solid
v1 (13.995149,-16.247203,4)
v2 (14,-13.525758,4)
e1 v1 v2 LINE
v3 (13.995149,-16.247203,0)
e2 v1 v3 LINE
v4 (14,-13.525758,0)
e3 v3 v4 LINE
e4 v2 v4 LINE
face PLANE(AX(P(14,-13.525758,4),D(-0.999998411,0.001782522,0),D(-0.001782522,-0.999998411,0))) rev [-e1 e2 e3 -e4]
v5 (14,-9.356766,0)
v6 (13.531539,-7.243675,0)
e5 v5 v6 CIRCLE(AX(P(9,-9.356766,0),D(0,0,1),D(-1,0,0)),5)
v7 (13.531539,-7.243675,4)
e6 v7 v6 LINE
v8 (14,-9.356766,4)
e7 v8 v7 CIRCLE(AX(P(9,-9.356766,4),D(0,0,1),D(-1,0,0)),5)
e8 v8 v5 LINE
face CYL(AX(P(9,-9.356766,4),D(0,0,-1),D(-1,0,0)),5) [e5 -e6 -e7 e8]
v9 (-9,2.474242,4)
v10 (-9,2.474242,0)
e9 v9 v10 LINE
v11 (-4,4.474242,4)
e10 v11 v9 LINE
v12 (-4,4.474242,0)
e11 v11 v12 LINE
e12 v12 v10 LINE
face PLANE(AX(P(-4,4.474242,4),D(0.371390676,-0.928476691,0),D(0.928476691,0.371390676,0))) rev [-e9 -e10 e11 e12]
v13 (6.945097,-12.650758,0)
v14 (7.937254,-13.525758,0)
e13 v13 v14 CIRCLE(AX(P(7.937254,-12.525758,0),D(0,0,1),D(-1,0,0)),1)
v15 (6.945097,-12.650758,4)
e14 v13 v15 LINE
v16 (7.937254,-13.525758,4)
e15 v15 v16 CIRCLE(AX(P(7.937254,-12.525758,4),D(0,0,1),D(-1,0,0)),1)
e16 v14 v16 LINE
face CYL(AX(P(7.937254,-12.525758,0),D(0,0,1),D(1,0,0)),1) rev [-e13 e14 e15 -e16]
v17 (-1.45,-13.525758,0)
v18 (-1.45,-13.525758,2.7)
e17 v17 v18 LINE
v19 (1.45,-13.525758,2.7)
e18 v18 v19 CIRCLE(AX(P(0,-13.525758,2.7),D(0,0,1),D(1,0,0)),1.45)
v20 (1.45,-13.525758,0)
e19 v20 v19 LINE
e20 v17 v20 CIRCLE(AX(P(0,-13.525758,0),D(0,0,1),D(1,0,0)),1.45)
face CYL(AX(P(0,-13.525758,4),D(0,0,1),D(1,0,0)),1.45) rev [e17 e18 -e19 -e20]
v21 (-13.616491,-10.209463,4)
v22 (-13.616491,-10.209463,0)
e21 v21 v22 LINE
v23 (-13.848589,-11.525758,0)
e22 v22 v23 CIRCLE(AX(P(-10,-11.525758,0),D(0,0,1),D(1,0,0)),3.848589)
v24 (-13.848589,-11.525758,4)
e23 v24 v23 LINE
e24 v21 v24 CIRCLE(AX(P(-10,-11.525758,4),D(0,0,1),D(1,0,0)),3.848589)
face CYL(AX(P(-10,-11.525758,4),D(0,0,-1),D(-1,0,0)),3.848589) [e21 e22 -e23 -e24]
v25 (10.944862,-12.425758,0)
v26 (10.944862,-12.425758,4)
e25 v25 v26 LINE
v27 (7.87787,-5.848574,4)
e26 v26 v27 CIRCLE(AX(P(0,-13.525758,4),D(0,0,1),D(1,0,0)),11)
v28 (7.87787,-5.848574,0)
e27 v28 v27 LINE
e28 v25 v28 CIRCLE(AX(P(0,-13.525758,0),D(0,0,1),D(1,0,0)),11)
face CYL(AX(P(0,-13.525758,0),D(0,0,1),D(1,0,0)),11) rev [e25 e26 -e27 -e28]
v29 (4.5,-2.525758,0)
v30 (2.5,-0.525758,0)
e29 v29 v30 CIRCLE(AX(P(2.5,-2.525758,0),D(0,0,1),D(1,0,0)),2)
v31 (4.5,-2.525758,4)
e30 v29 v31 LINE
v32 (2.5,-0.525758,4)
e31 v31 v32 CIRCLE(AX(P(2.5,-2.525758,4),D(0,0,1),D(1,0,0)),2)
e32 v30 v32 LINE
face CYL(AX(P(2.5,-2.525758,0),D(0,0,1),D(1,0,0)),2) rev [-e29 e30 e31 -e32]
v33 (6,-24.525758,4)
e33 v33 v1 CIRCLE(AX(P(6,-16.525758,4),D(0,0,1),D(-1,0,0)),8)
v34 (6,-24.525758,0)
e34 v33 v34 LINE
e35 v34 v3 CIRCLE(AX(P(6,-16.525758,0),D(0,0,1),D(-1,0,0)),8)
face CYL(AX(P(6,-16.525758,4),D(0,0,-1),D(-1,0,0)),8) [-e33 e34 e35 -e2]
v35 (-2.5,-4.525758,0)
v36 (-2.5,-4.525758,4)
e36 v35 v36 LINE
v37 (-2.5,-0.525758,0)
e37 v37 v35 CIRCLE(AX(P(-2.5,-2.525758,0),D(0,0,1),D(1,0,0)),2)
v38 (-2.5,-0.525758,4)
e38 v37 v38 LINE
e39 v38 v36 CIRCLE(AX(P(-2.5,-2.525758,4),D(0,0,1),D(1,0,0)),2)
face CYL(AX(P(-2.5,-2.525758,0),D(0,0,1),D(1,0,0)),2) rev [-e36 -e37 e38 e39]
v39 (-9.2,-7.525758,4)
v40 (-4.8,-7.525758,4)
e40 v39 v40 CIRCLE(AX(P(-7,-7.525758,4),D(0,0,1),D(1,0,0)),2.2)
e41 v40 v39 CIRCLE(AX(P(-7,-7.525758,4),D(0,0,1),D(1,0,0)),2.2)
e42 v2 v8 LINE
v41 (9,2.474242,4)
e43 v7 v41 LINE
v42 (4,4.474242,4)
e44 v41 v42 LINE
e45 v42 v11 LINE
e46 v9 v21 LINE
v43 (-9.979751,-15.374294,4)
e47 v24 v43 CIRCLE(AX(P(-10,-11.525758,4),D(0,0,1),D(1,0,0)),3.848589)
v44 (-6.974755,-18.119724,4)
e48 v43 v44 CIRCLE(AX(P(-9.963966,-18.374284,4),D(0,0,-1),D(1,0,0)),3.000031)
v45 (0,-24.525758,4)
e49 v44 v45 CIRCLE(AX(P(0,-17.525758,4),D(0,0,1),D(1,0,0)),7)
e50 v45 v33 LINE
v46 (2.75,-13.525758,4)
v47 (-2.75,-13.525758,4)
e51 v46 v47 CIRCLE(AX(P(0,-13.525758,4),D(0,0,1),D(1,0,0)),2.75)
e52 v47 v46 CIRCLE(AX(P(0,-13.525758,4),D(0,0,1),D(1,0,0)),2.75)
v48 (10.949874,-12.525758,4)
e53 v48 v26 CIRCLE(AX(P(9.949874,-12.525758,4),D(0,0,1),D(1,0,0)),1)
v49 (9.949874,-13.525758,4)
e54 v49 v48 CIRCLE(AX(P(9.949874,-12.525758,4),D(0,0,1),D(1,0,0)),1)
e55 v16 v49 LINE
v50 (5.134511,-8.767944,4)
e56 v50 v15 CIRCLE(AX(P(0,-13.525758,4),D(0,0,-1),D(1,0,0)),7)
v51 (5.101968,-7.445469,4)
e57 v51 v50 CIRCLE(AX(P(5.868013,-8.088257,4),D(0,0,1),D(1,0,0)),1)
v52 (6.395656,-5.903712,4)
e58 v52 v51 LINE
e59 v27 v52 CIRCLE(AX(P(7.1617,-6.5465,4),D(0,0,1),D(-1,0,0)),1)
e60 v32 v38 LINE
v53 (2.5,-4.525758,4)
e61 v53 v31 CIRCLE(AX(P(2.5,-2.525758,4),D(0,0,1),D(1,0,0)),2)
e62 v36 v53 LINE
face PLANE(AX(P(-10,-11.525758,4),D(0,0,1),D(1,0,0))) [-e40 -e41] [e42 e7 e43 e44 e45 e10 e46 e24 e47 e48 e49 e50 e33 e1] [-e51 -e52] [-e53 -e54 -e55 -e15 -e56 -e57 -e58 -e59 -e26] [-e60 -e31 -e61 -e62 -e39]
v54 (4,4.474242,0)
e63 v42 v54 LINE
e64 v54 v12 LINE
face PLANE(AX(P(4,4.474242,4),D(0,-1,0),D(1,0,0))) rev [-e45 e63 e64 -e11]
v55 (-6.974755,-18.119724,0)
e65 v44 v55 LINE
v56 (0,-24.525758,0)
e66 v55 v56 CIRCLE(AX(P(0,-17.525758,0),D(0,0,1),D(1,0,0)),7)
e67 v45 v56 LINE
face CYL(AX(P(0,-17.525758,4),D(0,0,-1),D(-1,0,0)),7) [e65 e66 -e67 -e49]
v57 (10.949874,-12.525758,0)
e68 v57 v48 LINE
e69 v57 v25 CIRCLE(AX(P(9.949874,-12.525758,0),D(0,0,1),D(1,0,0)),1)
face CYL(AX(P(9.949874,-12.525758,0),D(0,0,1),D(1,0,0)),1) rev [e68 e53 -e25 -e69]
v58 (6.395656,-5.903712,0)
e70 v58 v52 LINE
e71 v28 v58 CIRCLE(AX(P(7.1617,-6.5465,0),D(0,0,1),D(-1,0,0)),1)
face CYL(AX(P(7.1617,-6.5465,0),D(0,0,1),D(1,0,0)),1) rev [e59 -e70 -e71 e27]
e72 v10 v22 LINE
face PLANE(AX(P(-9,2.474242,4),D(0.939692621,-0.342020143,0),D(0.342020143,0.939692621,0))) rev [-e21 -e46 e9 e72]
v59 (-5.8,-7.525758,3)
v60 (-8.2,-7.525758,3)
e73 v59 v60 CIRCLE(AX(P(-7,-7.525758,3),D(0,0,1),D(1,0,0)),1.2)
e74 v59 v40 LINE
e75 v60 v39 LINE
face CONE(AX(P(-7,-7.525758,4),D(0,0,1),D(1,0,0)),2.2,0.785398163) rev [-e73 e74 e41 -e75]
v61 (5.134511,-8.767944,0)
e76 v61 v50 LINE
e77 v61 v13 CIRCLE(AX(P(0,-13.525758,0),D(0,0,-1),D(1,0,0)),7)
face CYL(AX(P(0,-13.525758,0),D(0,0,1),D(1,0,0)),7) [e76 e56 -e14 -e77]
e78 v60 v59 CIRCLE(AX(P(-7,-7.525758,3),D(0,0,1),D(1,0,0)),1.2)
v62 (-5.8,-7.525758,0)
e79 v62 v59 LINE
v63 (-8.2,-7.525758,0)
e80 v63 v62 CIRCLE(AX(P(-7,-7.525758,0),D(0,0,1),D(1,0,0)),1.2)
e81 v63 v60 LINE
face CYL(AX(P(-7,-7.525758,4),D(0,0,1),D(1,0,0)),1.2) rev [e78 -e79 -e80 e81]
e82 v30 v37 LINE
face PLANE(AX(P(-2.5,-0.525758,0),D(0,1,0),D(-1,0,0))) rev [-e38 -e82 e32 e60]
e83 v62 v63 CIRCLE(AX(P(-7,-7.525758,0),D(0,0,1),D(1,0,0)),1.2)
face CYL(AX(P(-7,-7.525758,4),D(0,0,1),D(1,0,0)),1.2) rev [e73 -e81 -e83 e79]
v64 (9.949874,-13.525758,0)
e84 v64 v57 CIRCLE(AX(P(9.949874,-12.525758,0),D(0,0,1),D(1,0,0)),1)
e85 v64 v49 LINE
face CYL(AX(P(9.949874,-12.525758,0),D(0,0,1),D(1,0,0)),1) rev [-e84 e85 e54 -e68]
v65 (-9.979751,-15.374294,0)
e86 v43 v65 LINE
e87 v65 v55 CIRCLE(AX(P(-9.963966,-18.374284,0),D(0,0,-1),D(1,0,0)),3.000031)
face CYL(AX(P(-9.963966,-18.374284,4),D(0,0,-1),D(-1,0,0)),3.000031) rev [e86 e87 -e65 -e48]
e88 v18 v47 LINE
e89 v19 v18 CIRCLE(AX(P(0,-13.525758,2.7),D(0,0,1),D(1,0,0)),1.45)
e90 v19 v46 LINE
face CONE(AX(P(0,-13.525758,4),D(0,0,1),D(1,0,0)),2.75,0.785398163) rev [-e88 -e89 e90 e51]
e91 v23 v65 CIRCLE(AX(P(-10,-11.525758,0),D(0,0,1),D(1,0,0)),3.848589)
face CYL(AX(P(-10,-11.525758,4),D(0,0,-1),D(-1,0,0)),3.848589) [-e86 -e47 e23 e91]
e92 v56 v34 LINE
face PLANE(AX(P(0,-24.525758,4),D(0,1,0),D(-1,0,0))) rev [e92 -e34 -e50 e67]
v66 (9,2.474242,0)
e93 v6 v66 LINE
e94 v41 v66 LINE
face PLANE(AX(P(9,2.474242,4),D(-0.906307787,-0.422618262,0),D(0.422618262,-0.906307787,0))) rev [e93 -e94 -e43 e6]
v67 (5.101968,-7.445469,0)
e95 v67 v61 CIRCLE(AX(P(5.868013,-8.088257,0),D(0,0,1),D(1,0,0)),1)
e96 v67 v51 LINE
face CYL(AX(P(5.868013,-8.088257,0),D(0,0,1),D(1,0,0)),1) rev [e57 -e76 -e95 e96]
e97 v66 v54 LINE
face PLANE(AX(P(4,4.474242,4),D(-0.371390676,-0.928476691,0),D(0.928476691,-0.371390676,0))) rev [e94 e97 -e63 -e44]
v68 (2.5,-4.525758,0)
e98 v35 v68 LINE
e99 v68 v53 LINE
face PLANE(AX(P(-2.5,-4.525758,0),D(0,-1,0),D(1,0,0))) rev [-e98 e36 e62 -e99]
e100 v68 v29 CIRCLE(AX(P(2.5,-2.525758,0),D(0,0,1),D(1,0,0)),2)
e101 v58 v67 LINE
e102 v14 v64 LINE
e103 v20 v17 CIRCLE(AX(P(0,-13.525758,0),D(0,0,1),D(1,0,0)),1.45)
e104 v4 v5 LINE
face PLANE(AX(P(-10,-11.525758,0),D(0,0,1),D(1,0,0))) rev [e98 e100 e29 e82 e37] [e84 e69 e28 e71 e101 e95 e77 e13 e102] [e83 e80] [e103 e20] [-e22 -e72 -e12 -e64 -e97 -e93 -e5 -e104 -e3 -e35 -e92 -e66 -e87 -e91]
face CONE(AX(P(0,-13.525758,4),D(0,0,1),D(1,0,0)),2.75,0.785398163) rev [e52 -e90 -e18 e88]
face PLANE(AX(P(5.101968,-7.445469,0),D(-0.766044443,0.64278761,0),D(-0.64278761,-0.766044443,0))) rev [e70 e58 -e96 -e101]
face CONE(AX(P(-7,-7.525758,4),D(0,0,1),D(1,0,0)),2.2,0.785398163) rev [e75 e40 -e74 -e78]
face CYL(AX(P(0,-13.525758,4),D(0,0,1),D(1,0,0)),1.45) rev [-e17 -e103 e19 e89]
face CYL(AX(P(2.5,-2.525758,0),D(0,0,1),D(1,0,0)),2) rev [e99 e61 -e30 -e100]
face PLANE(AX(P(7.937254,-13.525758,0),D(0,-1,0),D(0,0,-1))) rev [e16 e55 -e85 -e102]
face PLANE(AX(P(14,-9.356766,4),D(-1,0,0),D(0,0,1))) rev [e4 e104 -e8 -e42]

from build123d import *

# Parameters (mm, degrees)
CAM_PLATE_4MM_DEPTH       = 4
SLOTS_CUT_DEPTH           = 4
CSK_HOLE_M2_5_D           = 2.9
CSK_HOLE_M2_5_DEPTH       = 29
CSK_HOLE_M2_5_CSINK_D     = 5.5
CSK_HOLE_M2_5_CSINK_ANGLE = 90
CSK_HOLE_M2_5_TIP         = 0.871247898
CSK_HOLE_M2_D             = 2.4
CSK_HOLE_M2_DEPTH         = 29
CSK_HOLE_M2_CSINK_D       = 4.4
CSK_HOLE_M2_CSINK_ANGLE   = 90
CSK_HOLE_M2_TIP           = 0.721032743


with BuildPart() as part:
    # Cam Plate Profile Sketch → Cam Plate 4mm (new body)
    with BuildSketch(Plane.XY):
        with BuildLine():
            Line((4, 4.474241718), (-4, 4.474241718))
            Line((-4, 4.474241718), (-9, 2.474241718))
            Line((-9, 2.474241718), (-13.616491046, -10.209463189))
            ThreePointArc((-13.616491046, -10.209463189), (-13.146761684, -13.741504469), (-9.979750738, -15.374294397))
            ThreePointArc((-9.979750738, -15.374294397), (-7.940438794, -16.159442387), (-6.974754793, -18.11972425))
            ThreePointArc((-6.974754793, -18.11972425), (-4.735094414, -22.681229249), (0, -24.525758282))
            Line((0, -24.525758282), (6, -24.525758282))
            ThreePointArc((6, -24.525758282), (11.754495804, -22.083255744), (13.995148957, -16.247202791))
            Line((13.995148957, -16.247202791), (14, -13.525758282))
            Line((14, -13.525758282), (14, -9.356766198))
            ThreePointArc((14, -9.356766198), (13.881480036, -8.274568128), (13.531538935, -7.243674889))
            Line((13.531538935, -7.243674889), (9, 2.474241718))
            Line((9, 2.474241718), (4, 4.474241718))
        make_face()
    extrude(amount=CAM_PLATE_4MM_DEPTH)

    # Slot Profiles Sketch → Slots Cut (cut)
    with BuildSketch(Plane.XY.offset(4)):
        with BuildLine():
            Line((-2.5, -0.525758282), (2.5, -0.525758282))
            ThreePointArc((2.5, -0.525758282), (4.5, -2.525758282), (2.5, -4.525758282))
            Line((2.5, -4.525758282), (-2.5, -4.525758282))
            ThreePointArc((-2.5, -4.525758282), (-4.5, -2.525758282), (-2.5, -0.525758282))
        make_face()
        with BuildLine():
            Line((5.101968483, -7.445469013), (6.395655964, -5.90371231))
            ThreePointArc((6.395655964, -5.90371231), (7.124526222, -5.547191119), (7.877870447, -5.848574084))
            ThreePointArc((7.877870447, -5.848574084), (9.969385657, -8.876957403), (10.944861808, -12.425758282))
            ThreePointArc((10.944861808, -12.425758282), (10.69149422, -13.196578675), (9.949874371, -13.525758282))
            Line((9.949874371, -13.525758282), (7.937253933, -13.525758282))
            ThreePointArc((7.937253933, -13.525758282), (7.275816105, -13.275758282), (6.945097192, -12.650758282))
            ThreePointArc((6.945097192, -12.650758282), (6.344154509, -10.56743045), (5.134511311, -8.76794433))
            ThreePointArc((5.134511311, -8.76794433), (4.868315554, -8.112856688), (5.101968483, -7.445469013))
        make_face()
    extrude(amount=-SLOTS_CUT_DEPTH, mode=Mode.SUBTRACT)

    # CSK Hole M2.5
    with Locations(Plane(origin=(0, -13.525758282, 4), x_dir=(1, 0, 0), z_dir=(0, 0, 1))):
        with Locations((0, 0)):
            CounterSinkHole(CSK_HOLE_M2_5_D / 2, CSK_HOLE_M2_5_CSINK_D / 2, depth=CSK_HOLE_M2_5_DEPTH, counter_sink_angle=CSK_HOLE_M2_5_CSINK_ANGLE)
            with Locations((0, 0, -(CSK_HOLE_M2_5_DEPTH + CSK_HOLE_M2_5_TIP / 2))):  # 118° drill point
                Cone(0, CSK_HOLE_M2_5_D / 2, CSK_HOLE_M2_5_TIP, mode=Mode.SUBTRACT)

    # CSK Hole M2
    with Locations(Plane(origin=(-7, -7.525758282, 4), x_dir=(1, 0, 0), z_dir=(0, 0, 1))):
        with Locations((0, 0)):
            CounterSinkHole(CSK_HOLE_M2_D / 2, CSK_HOLE_M2_CSINK_D / 2, depth=CSK_HOLE_M2_DEPTH, counter_sink_angle=CSK_HOLE_M2_CSINK_ANGLE)
            with Locations((0, 0, -(CSK_HOLE_M2_DEPTH + CSK_HOLE_M2_TIP / 2))):  # 118° drill point
                Cone(0, CSK_HOLE_M2_D / 2, CSK_HOLE_M2_TIP, mode=Mode.SUBTRACT)


solid = part.part
